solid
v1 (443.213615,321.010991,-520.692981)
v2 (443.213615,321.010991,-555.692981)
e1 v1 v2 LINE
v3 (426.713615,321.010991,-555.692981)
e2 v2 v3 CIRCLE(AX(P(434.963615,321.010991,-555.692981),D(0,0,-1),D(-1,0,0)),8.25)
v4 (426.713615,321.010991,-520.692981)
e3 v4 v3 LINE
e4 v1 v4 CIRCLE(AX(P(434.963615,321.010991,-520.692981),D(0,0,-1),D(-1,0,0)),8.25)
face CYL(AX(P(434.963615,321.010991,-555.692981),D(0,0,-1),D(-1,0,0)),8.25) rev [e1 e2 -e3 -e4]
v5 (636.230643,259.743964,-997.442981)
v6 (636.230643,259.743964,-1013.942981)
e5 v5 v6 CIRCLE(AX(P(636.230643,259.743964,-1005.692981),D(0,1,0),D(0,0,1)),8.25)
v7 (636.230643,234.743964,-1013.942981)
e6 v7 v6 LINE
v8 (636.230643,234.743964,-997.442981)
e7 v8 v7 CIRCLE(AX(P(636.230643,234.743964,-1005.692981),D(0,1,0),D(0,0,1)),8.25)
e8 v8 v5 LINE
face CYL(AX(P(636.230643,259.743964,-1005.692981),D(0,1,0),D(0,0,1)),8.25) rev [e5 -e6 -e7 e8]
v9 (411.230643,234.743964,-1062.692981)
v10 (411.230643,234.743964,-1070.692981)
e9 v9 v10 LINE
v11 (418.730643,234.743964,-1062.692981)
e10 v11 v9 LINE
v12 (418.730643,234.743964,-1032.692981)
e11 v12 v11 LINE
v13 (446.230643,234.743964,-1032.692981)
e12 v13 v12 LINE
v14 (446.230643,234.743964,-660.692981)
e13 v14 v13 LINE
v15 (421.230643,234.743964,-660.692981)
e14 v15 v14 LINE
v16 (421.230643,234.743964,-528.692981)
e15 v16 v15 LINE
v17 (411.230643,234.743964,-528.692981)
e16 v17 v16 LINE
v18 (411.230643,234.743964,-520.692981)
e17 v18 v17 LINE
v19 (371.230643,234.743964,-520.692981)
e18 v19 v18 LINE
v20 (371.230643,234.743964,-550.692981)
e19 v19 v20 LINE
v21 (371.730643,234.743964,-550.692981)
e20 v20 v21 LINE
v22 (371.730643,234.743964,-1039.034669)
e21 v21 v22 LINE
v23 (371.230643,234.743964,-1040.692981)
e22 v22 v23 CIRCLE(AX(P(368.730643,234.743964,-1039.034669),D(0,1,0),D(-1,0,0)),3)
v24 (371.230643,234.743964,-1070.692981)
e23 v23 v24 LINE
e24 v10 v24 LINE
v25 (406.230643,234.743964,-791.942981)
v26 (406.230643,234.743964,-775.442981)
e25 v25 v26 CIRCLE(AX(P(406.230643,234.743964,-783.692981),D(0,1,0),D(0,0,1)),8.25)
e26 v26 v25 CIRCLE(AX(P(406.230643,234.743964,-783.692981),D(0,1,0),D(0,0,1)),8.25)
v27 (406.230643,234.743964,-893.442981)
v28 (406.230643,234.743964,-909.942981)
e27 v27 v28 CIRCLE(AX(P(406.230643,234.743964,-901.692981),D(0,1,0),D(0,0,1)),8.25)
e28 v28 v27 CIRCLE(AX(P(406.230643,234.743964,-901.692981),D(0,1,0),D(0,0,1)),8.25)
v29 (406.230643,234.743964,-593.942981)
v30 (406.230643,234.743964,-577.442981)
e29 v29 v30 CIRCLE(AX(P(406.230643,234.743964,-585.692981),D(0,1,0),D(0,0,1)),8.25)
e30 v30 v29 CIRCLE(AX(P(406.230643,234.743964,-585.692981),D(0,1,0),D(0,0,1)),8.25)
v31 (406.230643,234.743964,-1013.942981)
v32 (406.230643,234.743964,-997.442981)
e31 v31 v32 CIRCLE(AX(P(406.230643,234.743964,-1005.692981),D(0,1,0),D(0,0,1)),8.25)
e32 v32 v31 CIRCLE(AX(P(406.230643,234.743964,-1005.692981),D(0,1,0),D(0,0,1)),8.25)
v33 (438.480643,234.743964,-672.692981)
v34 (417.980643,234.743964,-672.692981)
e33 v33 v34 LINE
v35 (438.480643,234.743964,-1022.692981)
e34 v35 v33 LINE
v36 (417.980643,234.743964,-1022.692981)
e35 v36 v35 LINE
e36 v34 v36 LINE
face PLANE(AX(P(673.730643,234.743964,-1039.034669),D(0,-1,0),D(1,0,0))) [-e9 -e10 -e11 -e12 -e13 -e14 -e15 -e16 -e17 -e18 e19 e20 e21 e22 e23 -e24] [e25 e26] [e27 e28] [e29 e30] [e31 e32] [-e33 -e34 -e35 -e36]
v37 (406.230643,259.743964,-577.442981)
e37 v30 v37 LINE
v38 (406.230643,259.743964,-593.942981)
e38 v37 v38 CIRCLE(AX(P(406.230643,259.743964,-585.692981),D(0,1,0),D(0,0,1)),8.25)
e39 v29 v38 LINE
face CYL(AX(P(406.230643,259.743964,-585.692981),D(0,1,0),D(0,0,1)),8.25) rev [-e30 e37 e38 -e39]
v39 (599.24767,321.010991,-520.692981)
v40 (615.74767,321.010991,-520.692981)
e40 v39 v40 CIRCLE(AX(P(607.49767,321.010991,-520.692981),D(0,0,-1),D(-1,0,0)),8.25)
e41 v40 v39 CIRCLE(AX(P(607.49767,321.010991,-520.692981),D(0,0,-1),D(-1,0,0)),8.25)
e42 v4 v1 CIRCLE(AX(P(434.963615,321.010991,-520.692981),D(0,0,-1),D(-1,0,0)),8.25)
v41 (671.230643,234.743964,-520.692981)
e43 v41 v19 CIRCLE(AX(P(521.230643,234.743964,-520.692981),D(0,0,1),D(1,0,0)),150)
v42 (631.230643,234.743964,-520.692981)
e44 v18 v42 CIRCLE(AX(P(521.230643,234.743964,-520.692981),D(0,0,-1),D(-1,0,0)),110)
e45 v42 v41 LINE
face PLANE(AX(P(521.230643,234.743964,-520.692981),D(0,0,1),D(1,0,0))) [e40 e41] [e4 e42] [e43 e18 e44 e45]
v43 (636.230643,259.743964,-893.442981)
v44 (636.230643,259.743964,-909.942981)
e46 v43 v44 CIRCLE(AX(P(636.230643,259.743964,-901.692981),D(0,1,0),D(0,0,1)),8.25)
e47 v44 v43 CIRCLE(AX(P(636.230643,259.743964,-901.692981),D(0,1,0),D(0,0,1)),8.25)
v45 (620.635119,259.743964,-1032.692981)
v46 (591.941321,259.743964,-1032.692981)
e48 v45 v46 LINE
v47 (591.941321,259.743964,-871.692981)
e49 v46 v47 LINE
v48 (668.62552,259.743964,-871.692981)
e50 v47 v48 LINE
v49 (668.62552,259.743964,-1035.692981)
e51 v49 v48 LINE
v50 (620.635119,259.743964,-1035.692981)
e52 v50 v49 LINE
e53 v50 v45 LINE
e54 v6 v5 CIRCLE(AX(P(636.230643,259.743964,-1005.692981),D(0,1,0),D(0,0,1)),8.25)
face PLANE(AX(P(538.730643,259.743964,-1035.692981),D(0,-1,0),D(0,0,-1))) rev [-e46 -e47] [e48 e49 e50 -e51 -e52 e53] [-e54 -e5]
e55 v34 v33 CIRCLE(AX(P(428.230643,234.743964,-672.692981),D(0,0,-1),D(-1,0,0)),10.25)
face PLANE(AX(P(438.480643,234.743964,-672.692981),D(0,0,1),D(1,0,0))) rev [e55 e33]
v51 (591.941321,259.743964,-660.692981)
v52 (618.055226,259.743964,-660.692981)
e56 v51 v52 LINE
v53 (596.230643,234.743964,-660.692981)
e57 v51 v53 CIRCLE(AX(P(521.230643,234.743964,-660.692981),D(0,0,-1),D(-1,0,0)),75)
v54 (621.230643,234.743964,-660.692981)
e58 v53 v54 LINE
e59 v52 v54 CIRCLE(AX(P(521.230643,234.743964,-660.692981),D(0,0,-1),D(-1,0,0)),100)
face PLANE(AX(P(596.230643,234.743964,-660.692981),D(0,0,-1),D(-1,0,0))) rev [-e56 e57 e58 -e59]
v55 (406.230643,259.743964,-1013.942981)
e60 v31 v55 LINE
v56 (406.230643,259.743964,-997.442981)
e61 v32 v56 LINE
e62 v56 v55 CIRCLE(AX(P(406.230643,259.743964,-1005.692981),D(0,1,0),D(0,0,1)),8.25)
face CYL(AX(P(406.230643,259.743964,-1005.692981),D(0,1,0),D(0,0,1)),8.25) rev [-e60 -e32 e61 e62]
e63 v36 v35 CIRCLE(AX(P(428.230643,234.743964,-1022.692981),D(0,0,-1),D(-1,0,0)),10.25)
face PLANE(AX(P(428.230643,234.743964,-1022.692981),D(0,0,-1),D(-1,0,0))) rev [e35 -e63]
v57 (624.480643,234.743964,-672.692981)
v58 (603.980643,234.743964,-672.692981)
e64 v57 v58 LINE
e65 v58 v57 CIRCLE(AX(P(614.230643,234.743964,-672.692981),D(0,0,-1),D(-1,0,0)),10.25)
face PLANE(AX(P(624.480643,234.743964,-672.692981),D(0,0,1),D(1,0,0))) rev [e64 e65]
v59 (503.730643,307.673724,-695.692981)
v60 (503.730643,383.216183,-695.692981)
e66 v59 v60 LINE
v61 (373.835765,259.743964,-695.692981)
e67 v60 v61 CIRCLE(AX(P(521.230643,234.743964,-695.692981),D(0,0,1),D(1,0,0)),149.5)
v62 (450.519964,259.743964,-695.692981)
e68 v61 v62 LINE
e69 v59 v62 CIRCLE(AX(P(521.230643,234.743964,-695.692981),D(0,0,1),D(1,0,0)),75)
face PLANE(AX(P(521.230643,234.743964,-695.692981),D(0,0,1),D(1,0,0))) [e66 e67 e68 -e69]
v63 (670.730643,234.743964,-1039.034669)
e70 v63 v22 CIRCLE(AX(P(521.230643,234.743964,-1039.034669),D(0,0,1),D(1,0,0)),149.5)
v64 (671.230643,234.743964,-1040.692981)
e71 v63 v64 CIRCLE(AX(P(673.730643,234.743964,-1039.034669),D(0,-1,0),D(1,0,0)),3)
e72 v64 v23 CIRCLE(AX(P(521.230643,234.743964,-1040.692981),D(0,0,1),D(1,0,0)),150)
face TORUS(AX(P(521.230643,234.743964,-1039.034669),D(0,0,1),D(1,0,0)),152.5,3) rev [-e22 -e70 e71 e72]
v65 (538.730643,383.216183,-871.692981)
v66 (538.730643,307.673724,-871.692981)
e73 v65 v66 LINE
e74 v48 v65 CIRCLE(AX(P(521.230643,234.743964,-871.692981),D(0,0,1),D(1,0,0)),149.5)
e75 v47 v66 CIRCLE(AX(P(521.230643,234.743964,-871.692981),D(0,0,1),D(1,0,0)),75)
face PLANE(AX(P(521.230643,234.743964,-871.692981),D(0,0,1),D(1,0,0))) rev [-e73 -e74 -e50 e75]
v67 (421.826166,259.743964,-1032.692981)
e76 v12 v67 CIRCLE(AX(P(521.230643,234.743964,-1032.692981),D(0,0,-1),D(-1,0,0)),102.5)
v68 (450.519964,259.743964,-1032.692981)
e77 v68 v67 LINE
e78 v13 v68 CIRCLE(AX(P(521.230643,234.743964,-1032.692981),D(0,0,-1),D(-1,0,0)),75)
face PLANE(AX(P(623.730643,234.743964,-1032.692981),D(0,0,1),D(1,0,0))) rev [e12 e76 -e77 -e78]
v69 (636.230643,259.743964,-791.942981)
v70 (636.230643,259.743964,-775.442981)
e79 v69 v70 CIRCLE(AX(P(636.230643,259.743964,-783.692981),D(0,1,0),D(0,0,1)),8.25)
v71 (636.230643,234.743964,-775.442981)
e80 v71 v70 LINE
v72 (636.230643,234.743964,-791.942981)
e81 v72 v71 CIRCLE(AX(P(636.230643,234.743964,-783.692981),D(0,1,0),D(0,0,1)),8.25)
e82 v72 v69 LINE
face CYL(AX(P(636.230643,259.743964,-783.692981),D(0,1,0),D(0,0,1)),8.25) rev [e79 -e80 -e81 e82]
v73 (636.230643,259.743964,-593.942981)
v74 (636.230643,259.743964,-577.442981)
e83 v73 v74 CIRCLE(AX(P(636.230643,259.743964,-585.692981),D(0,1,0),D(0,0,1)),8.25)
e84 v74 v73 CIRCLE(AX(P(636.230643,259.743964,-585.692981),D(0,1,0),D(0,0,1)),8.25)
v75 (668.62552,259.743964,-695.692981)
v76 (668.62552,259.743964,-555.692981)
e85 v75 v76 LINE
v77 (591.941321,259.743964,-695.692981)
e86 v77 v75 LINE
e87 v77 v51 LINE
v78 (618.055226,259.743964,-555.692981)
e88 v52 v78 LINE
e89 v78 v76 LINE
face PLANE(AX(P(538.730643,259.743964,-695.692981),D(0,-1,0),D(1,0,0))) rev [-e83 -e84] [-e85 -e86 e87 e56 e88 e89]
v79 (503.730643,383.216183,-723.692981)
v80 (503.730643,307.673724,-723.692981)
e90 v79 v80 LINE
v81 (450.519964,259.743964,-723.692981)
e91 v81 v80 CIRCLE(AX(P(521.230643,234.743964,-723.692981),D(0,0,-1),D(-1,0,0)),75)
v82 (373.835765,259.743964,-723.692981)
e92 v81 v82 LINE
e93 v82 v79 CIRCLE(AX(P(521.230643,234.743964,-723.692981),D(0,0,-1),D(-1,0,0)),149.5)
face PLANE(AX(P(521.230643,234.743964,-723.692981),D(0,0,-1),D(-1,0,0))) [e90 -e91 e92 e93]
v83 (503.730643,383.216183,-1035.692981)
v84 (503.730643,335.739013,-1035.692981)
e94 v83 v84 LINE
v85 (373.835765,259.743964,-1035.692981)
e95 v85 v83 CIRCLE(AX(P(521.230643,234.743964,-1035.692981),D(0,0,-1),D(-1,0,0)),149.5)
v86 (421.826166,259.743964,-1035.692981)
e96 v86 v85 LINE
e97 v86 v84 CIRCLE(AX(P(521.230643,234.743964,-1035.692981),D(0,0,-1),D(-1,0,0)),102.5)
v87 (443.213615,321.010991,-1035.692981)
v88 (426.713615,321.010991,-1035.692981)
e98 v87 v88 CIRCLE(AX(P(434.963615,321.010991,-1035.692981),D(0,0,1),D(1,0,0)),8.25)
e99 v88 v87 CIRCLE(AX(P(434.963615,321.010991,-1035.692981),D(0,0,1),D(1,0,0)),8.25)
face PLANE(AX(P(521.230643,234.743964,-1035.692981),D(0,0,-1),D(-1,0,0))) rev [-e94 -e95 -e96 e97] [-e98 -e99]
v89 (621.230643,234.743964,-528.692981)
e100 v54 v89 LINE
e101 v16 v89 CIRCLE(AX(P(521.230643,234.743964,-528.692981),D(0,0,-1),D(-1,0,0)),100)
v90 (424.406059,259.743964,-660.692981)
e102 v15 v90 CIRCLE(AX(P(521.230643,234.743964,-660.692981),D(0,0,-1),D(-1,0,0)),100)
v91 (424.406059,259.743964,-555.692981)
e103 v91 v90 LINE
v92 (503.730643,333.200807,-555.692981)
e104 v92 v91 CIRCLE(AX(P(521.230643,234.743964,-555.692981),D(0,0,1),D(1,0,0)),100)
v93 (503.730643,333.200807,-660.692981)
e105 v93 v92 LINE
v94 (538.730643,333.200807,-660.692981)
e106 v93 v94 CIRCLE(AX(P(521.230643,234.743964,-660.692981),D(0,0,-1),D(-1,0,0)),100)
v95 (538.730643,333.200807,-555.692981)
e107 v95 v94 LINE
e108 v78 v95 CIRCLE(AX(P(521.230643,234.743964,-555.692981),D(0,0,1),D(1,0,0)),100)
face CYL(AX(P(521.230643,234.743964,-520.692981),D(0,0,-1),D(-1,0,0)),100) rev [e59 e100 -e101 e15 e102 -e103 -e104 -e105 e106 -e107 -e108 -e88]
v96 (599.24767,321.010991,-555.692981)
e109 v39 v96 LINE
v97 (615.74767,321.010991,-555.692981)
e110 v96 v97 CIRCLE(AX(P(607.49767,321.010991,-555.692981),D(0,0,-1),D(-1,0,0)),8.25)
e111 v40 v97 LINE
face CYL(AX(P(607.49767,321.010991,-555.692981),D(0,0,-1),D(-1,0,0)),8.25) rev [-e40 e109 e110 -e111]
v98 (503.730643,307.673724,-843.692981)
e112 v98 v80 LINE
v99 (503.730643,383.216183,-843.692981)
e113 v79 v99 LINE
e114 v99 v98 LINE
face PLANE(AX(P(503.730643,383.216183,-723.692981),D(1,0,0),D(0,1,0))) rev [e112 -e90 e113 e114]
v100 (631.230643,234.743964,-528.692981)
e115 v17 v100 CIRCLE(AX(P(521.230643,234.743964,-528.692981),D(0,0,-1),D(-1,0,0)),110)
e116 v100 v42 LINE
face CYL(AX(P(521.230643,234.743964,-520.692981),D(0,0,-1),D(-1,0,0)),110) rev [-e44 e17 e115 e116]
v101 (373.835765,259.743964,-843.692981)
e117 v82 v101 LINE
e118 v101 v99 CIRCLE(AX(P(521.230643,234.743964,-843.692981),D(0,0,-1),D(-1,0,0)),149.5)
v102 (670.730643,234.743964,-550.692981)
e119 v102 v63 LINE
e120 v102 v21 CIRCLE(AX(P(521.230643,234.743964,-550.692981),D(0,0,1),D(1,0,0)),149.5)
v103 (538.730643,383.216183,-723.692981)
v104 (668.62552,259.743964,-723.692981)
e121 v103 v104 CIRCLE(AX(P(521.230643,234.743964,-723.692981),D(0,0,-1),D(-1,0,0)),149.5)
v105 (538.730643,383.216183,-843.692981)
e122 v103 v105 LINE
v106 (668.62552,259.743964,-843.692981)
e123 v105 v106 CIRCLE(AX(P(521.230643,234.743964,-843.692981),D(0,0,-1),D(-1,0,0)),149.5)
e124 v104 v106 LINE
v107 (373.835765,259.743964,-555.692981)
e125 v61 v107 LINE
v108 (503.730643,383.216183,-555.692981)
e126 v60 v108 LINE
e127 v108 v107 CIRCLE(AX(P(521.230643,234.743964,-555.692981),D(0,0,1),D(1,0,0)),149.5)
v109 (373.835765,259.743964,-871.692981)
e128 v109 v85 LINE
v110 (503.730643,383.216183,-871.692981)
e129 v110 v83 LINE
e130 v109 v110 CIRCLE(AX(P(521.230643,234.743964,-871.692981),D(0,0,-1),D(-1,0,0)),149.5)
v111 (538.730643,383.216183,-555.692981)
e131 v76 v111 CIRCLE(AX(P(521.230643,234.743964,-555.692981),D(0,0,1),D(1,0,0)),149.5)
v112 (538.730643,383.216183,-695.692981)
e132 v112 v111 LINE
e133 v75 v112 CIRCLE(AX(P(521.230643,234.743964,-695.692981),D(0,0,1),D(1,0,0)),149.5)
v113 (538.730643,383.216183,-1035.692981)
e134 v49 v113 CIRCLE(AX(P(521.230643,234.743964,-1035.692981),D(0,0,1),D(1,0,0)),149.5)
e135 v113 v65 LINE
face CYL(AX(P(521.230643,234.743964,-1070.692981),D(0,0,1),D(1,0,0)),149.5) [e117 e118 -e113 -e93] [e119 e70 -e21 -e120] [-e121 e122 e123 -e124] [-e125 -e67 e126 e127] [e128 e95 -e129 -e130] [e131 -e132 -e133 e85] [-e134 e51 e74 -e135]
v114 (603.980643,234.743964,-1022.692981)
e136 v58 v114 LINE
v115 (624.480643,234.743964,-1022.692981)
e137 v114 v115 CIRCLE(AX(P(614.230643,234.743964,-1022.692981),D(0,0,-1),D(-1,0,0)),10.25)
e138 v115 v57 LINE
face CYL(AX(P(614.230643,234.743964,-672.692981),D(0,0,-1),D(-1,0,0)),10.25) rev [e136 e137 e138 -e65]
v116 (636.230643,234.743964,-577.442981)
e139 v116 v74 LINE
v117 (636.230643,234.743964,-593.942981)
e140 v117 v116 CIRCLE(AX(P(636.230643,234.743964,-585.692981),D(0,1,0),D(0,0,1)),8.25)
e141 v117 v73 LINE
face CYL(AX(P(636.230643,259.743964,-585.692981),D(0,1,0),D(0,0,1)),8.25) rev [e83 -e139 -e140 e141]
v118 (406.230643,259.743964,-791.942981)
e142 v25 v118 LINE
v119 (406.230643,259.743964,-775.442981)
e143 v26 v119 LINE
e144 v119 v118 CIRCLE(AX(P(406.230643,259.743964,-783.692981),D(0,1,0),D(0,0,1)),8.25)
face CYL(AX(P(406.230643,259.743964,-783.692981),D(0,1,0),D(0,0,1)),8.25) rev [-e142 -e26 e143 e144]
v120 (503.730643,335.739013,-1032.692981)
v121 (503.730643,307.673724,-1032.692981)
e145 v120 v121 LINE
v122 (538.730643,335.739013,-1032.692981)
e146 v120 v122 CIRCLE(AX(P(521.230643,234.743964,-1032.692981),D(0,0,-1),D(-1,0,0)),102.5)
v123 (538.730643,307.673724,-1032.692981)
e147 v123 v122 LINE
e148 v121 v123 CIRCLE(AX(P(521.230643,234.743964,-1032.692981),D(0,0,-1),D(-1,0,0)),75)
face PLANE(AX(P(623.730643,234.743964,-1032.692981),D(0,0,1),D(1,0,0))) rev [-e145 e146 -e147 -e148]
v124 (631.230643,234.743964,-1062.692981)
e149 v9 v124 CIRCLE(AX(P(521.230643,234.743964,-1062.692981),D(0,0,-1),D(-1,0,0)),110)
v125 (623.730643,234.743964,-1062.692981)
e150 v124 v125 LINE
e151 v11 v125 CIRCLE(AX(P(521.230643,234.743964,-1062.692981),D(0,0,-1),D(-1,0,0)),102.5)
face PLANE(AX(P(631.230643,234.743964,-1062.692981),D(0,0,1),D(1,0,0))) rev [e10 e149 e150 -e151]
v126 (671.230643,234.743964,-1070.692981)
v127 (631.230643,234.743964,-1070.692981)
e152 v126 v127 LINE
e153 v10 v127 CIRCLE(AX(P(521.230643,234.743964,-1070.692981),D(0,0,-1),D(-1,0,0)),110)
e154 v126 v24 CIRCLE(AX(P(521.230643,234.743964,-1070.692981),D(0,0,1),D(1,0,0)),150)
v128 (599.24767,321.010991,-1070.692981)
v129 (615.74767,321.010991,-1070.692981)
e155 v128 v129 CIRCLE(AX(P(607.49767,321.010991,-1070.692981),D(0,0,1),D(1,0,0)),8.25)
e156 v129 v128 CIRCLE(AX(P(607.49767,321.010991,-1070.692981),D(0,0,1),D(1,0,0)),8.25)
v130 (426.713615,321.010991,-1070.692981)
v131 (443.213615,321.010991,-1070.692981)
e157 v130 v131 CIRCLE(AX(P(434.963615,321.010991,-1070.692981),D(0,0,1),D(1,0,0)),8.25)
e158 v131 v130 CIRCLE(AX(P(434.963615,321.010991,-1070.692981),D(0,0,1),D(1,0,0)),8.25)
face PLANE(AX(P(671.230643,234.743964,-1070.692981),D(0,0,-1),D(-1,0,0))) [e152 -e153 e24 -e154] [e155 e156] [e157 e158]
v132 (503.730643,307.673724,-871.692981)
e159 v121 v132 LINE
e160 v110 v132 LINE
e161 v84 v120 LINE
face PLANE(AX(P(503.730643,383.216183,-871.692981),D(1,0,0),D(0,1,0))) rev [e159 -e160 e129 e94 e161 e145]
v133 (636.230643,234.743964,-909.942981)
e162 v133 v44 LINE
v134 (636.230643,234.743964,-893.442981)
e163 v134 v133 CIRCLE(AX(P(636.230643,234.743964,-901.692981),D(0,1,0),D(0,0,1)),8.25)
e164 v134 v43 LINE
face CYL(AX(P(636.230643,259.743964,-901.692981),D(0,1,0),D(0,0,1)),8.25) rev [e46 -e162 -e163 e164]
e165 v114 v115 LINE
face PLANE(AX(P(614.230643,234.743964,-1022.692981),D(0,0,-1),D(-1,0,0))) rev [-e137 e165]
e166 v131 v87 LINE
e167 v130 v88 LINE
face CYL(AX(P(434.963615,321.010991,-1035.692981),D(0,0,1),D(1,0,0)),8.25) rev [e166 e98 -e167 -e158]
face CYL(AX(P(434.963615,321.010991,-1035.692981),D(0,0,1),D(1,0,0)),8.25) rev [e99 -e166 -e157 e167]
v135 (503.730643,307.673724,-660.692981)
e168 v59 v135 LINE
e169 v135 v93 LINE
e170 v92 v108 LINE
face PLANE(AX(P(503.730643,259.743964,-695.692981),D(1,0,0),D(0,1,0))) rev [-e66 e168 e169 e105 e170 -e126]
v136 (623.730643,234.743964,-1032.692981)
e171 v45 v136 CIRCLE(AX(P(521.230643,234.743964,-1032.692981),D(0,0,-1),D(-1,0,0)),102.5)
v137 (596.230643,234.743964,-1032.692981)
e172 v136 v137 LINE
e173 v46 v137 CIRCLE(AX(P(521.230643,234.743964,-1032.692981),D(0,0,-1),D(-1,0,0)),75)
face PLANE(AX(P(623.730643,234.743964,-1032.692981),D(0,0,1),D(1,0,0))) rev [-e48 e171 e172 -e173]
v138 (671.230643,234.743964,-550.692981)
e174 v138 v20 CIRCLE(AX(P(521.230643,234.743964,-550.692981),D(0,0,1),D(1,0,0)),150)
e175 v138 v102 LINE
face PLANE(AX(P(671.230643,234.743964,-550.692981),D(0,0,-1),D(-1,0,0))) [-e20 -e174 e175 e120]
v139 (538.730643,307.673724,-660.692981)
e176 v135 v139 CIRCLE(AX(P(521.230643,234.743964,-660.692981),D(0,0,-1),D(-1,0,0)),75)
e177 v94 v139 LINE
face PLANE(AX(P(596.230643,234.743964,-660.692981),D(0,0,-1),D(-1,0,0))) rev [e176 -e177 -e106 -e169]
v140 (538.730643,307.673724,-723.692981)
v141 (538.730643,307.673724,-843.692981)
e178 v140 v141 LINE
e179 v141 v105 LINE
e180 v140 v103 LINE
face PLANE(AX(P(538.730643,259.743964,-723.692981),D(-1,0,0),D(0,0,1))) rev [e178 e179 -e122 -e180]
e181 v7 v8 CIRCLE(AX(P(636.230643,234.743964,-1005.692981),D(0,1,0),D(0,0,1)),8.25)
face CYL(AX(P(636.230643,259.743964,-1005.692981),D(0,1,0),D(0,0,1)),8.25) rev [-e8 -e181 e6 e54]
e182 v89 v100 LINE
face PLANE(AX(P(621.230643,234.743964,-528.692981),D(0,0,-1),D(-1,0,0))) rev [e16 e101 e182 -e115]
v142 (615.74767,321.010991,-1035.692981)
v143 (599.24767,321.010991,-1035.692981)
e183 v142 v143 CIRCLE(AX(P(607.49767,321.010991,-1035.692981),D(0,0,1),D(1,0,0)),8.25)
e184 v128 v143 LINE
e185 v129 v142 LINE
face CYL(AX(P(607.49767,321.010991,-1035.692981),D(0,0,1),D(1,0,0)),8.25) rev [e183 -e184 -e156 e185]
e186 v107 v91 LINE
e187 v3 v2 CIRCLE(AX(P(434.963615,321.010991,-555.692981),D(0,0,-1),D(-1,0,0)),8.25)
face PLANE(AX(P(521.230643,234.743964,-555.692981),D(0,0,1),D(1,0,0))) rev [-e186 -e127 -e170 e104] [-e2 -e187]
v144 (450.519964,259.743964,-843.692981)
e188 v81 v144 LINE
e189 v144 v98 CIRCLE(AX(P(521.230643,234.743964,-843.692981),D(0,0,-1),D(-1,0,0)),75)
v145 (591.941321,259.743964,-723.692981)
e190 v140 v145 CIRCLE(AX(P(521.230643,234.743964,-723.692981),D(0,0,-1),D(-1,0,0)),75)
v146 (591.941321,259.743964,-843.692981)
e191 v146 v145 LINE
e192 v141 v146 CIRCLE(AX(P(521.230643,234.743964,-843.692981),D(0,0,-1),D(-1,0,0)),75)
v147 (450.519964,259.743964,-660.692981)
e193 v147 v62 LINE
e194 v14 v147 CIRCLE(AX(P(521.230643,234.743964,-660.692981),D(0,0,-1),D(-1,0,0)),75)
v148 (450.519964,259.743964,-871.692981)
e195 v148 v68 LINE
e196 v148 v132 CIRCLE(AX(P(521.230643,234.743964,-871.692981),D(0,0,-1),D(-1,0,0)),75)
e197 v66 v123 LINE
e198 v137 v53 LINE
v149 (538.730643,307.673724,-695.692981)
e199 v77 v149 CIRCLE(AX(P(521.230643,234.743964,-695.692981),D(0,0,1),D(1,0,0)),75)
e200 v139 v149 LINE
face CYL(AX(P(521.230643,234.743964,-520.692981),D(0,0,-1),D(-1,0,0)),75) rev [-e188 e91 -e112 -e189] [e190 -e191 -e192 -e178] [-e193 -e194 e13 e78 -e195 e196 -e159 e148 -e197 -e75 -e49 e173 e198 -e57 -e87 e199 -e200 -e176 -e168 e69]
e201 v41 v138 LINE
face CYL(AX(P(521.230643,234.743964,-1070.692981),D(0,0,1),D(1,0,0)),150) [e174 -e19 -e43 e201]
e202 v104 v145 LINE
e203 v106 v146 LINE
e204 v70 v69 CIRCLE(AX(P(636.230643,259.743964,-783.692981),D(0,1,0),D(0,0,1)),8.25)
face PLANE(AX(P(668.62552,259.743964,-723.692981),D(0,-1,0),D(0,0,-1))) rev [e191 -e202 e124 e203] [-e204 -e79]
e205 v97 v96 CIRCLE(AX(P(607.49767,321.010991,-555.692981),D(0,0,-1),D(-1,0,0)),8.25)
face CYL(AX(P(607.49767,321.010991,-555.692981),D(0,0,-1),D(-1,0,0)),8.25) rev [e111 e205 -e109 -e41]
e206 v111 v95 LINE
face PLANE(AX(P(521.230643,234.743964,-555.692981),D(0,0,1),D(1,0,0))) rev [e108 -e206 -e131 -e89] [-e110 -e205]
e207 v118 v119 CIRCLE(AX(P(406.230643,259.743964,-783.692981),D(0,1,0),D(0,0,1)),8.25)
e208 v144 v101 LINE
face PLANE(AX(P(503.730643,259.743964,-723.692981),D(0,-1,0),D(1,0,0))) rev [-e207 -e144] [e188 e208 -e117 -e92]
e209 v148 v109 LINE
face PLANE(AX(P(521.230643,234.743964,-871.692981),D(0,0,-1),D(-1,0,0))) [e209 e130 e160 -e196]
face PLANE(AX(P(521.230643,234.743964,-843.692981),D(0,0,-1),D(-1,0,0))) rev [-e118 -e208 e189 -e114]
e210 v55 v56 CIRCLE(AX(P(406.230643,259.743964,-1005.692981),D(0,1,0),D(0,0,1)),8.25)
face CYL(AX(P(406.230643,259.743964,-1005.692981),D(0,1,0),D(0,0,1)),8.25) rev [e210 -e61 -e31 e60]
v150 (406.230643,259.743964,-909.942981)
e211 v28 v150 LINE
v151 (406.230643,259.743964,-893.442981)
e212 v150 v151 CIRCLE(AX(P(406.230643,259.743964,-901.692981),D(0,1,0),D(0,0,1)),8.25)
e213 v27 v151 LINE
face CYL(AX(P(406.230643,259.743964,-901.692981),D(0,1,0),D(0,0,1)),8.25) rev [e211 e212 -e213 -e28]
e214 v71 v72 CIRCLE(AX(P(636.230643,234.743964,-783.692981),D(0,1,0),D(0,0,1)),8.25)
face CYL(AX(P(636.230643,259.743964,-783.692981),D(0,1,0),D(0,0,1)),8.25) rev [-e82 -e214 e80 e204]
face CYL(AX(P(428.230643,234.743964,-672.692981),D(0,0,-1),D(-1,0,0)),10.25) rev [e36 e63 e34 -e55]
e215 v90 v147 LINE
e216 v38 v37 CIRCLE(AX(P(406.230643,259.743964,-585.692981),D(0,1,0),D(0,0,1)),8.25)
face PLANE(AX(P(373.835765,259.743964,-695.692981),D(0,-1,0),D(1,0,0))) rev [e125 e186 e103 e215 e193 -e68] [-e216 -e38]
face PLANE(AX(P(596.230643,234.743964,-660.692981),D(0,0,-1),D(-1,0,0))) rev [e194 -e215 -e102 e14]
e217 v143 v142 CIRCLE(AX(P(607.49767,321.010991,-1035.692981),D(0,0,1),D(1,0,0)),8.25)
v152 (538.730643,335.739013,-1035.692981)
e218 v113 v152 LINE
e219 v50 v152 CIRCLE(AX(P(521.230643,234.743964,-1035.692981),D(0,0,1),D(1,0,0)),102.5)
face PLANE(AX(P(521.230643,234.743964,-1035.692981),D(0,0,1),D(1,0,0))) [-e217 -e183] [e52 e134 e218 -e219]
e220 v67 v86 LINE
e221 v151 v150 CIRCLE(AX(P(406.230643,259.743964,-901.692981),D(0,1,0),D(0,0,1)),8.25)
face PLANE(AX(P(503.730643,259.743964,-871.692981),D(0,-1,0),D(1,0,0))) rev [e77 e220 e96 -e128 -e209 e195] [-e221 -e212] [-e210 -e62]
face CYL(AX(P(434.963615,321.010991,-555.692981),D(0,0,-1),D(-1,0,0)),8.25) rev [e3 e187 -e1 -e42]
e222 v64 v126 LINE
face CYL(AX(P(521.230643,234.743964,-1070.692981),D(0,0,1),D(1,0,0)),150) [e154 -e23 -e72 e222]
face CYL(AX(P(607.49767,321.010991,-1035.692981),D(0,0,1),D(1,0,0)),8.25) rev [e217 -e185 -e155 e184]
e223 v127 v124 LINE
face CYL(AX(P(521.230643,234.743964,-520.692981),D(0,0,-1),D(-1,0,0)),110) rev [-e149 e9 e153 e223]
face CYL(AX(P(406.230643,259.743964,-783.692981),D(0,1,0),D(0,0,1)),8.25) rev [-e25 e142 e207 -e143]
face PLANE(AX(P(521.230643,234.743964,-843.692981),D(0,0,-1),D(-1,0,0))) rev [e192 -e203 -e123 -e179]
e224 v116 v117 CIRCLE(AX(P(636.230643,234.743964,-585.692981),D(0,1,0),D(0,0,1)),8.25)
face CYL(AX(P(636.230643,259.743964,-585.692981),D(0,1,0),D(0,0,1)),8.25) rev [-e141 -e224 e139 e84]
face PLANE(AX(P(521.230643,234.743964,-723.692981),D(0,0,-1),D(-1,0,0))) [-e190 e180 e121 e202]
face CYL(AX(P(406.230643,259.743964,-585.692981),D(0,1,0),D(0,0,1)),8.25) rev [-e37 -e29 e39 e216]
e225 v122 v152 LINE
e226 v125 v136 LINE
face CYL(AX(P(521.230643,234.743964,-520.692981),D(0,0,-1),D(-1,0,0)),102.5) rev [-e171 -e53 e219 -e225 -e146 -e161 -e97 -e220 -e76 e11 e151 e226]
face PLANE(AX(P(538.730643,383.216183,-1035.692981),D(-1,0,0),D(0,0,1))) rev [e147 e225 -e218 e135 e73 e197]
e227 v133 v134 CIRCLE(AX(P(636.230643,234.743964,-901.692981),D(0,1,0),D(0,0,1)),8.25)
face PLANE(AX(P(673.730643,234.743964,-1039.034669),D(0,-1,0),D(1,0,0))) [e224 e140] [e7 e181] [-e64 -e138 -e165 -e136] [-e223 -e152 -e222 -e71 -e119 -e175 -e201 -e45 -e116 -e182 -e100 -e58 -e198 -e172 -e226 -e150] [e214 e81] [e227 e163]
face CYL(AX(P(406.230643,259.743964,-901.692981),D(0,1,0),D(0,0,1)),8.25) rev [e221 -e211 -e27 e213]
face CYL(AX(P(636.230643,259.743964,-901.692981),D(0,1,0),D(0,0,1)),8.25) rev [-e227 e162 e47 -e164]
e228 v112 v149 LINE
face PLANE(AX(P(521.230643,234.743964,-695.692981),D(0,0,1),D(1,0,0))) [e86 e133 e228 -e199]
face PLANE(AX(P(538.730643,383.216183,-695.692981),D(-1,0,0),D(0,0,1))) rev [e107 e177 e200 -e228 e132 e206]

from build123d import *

# Parameters (mm, degrees)
REVOLVE1_ANGLE                   = 180
CUT_EXTRUDE1_DEPTH               = 164
CUT_EXTRUDE2_START               = -164
CUT_EXTRUDE2_DEPTH               = 164
CUT_EXTRUDE3_START               = -140
CUT_EXTRUDE3_DEPTH               = 140
CUT_EXTRUDE4_DEPTH               = 120
CUT_EXTRUDE5_START               = -140
CUT_EXTRUDE5_DEPTH               = 140
CUT_EXTRUDE6_DEPTH               = 120
SKETCH9_W                        = 10.25
SKETCH9_H                        = 350
SKETCH10_W                       = 10.25
SKETCH10_H                       = 350
F_16_5_16_5_DIAMETER_HOLE1_D     = 16.5
F_16_5_16_5_DIAMETER_HOLE2_D     = 16.5
F_16_5_16_5_DIAMETER_HOLE2_DEPTH = 35
F_16_5_16_5_DIAMETER_HOLE3_D     = 16.5
F_16_5_16_5_DIAMETER_HOLE3_DEPTH = 35


with BuildPart() as part:
    # Sketch1 → Revolve1 (revolve)
    with BuildSketch(Plane.XZ.offset(-234.743963655)):
        with BuildLine():
            Line((371.230642584, -1070.692981355), (521.230642584, -1070.692981355))
            Line((521.230642584, -1070.692981355), (521.230642584, -520.692981355))
            Line((521.230642584, -520.692981355), (371.230642584, -520.692981355))
            Line((371.230642584, -520.692981355), (371.230642584, -550.692981355))
            Line((371.230642584, -550.692981355), (371.730642584, -550.692981355))
            Line((371.730642584, -550.692981355), (371.730642584, -1039.03466896))
            ThreePointArc((371.730642584, -1039.03466896), (371.602923908, -1039.900694364), (371.230642584, -1040.692981355))
            Line((371.230642584, -1040.692981355), (371.230642584, -1070.692981355))
        make_face()
    revolve(axis=Axis((521.230642584, 234.743963655, -1070.692981355), (0, 0, -1)), revolution_arc=REVOLVE1_ANGLE)

    # Sketch2 → Cut-Extrude1 (cut)
    with BuildSketch(Plane(origin=(0, 0, -1035.692981355), x_dir=(-1, 0, 0), z_dir=(0, 0, -1))):
        with BuildLine():
            Line((-503.730642584, 383.216183278), (-503.730642584, 259.743963655))
            Line((-503.730642584, 259.743963655), (-373.83576479, 259.743963655))
            ThreePointArc((-373.83576479, 259.743963655), (-418.23099484, 343.10134718), (-503.730642584, 383.216183278))
        make_face()
    extrude(amount=-CUT_EXTRUDE1_DEPTH, mode=Mode.SUBTRACT)

    # Sketch3 → Cut-Extrude2 (cut)
    with BuildSketch(Plane.XY.offset(-871.692981355).offset(CUT_EXTRUDE2_START)):
        with BuildLine():
            Line((538.730642584, 383.216183278), (538.730642584, 259.743963655))
            Line((538.730642584, 259.743963655), (668.625520379, 259.743963655))
            ThreePointArc((668.625520379, 259.743963655), (624.230290328, 343.10134718), (538.730642584, 383.216183278))
        make_face()
    extrude(amount=CUT_EXTRUDE2_DEPTH, mode=Mode.SUBTRACT)

    # Sketch4 → Cut-Extrude3 (cut)
    with BuildSketch(Plane.XY.offset(-555.692981355).offset(CUT_EXTRUDE3_START)):
        with BuildLine():
            Line((503.730642584, 259.743963655), (503.730642584, 383.216183278))
            ThreePointArc((503.730642584, 383.216183278), (418.23099484, 343.10134718), (373.83576479, 259.743963655))
            Line((373.83576479, 259.743963655), (503.730642584, 259.743963655))
        make_face()
    extrude(amount=CUT_EXTRUDE3_DEPTH, mode=Mode.SUBTRACT)

    # Sketch5 → Cut-Extrude4 (cut)
    with BuildSketch(Plane(origin=(0, 0, -843.692981355), x_dir=(-1, 0, 0), z_dir=(0, 0, -1))):
        with BuildLine():
            Line((-503.730642584, 259.743963655), (-373.83576479, 259.743963655))
            ThreePointArc((-373.83576479, 259.743963655), (-418.23099484, 343.10134718), (-503.730642584, 383.216183278))
            Line((-503.730642584, 383.216183278), (-503.730642584, 259.743963655))
        make_face()
    extrude(amount=-CUT_EXTRUDE4_DEPTH, mode=Mode.SUBTRACT)

    # Sketch6 → Cut-Extrude5 (cut)
    with BuildSketch(Plane.XY.offset(-555.692981355).offset(CUT_EXTRUDE5_START)):
        with BuildLine():
            Line((538.730642584, 259.743963655), (668.625520379, 259.743963655))
            ThreePointArc((668.625520379, 259.743963655), (624.230290328, 343.10134718), (538.730642584, 383.216183278))
            Line((538.730642584, 383.216183278), (538.730642584, 259.743963655))
        make_face()
    extrude(amount=CUT_EXTRUDE5_DEPTH, mode=Mode.SUBTRACT)

    # Sketch7 → Cut-Extrude6 (cut)
    with BuildSketch(Plane(origin=(0, 0, -843.692981355), x_dir=(-1, 0, 0), z_dir=(0, 0, -1))):
        with BuildLine():
            Line((-538.730642584, 259.743963655), (-538.730642584, 383.216183278))
            ThreePointArc((-538.730642584, 383.216183278), (-624.230290328, 343.10134718), (-668.625520379, 259.743963655))
            Line((-668.625520379, 259.743963655), (-538.730642584, 259.743963655))
        make_face()
    extrude(amount=-CUT_EXTRUDE6_DEPTH, mode=Mode.SUBTRACT)

    # Sketch8 → Cut-Revolve1 (revolve, cut)
    with BuildSketch(Plane.XZ.offset(-234.743963655)):
        Polygon((631.230642584, -520.692981355), (521.230642584, -520.692981355), (521.230642584, -1070.692981355), (631.230642584, -1070.692981355), (631.230642584, -1062.692981355), (623.730642584, -1062.692981355), (623.730642584, -1032.692981355), (596.230642584, -1032.692981355), (596.230642584, -660.692981355), (621.230642584, -660.692981355), (621.230642584, -528.692981355), (631.230642584, -528.692981355), align=None)
    revolve(axis=Axis((521.230642584, 234.743963655, -520.692981355), (0, 0, -1)), mode=Mode.SUBTRACT)

    # Sketch9 → Cut-Revolve2 (revolve, cut)
    with BuildSketch(Plane.XZ.offset(-234.743963655)):
        with Locations((619.355642584, -847.692981355)):
            Rectangle(SKETCH9_W, SKETCH9_H)
    revolve(axis=Axis((614.230642584, 234.743963655, -672.692981355), (0, 0, -1)), mode=Mode.SUBTRACT)

    # Sketch10 → Cut-Revolve3 (revolve, cut)
    with BuildSketch(Plane.XZ.offset(-234.743963655)):
        with Locations((433.355642584, -847.692981355)):
            Rectangle(SKETCH10_W, SKETCH10_H)
    revolve(axis=Axis((428.230642584, 234.743963655, -672.692981355), (0, 0, -1)), mode=Mode.SUBTRACT)

    # Ø16.5 (16.5) diameter hole1 (through all)
    with Locations(Plane(origin=(0, 259.743963655, 0), x_dir=(1, 0, 0), z_dir=(0, 1, 0))):
        with Locations((636.230642584, 1005.692981355), (636.230642584, 901.692981355), (636.230642584, 783.692981355), (636.230642584, 585.692981355), (406.230642584, 1005.692981355), (406.230642584, 901.692981355), (406.230642584, 585.692981355), (406.230642584, 783.692981355)):
            Hole(F_16_5_16_5_DIAMETER_HOLE1_D / 2)

    # Ø16.5 (16.5) diameter hole2
    with Locations(Plane.XY.offset(-1035.692981355)):
        with Locations((607.497669889, 321.010990959), (434.96361528, 321.010990959)):
            Hole(F_16_5_16_5_DIAMETER_HOLE2_D / 2, depth=F_16_5_16_5_DIAMETER_HOLE2_DEPTH)

    # Ø16.5 (16.5) diameter hole3
    with Locations(Plane(origin=(0, 0, -555.692981355), x_dir=(-1, 0, 0), z_dir=(0, 0, -1))):
        with Locations((-607.497669889, 321.010990959), (-434.96361528, 321.010990959)):
            Hole(F_16_5_16_5_DIAMETER_HOLE3_D / 2, depth=F_16_5_16_5_DIAMETER_HOLE3_DEPTH)


solid = part.part
